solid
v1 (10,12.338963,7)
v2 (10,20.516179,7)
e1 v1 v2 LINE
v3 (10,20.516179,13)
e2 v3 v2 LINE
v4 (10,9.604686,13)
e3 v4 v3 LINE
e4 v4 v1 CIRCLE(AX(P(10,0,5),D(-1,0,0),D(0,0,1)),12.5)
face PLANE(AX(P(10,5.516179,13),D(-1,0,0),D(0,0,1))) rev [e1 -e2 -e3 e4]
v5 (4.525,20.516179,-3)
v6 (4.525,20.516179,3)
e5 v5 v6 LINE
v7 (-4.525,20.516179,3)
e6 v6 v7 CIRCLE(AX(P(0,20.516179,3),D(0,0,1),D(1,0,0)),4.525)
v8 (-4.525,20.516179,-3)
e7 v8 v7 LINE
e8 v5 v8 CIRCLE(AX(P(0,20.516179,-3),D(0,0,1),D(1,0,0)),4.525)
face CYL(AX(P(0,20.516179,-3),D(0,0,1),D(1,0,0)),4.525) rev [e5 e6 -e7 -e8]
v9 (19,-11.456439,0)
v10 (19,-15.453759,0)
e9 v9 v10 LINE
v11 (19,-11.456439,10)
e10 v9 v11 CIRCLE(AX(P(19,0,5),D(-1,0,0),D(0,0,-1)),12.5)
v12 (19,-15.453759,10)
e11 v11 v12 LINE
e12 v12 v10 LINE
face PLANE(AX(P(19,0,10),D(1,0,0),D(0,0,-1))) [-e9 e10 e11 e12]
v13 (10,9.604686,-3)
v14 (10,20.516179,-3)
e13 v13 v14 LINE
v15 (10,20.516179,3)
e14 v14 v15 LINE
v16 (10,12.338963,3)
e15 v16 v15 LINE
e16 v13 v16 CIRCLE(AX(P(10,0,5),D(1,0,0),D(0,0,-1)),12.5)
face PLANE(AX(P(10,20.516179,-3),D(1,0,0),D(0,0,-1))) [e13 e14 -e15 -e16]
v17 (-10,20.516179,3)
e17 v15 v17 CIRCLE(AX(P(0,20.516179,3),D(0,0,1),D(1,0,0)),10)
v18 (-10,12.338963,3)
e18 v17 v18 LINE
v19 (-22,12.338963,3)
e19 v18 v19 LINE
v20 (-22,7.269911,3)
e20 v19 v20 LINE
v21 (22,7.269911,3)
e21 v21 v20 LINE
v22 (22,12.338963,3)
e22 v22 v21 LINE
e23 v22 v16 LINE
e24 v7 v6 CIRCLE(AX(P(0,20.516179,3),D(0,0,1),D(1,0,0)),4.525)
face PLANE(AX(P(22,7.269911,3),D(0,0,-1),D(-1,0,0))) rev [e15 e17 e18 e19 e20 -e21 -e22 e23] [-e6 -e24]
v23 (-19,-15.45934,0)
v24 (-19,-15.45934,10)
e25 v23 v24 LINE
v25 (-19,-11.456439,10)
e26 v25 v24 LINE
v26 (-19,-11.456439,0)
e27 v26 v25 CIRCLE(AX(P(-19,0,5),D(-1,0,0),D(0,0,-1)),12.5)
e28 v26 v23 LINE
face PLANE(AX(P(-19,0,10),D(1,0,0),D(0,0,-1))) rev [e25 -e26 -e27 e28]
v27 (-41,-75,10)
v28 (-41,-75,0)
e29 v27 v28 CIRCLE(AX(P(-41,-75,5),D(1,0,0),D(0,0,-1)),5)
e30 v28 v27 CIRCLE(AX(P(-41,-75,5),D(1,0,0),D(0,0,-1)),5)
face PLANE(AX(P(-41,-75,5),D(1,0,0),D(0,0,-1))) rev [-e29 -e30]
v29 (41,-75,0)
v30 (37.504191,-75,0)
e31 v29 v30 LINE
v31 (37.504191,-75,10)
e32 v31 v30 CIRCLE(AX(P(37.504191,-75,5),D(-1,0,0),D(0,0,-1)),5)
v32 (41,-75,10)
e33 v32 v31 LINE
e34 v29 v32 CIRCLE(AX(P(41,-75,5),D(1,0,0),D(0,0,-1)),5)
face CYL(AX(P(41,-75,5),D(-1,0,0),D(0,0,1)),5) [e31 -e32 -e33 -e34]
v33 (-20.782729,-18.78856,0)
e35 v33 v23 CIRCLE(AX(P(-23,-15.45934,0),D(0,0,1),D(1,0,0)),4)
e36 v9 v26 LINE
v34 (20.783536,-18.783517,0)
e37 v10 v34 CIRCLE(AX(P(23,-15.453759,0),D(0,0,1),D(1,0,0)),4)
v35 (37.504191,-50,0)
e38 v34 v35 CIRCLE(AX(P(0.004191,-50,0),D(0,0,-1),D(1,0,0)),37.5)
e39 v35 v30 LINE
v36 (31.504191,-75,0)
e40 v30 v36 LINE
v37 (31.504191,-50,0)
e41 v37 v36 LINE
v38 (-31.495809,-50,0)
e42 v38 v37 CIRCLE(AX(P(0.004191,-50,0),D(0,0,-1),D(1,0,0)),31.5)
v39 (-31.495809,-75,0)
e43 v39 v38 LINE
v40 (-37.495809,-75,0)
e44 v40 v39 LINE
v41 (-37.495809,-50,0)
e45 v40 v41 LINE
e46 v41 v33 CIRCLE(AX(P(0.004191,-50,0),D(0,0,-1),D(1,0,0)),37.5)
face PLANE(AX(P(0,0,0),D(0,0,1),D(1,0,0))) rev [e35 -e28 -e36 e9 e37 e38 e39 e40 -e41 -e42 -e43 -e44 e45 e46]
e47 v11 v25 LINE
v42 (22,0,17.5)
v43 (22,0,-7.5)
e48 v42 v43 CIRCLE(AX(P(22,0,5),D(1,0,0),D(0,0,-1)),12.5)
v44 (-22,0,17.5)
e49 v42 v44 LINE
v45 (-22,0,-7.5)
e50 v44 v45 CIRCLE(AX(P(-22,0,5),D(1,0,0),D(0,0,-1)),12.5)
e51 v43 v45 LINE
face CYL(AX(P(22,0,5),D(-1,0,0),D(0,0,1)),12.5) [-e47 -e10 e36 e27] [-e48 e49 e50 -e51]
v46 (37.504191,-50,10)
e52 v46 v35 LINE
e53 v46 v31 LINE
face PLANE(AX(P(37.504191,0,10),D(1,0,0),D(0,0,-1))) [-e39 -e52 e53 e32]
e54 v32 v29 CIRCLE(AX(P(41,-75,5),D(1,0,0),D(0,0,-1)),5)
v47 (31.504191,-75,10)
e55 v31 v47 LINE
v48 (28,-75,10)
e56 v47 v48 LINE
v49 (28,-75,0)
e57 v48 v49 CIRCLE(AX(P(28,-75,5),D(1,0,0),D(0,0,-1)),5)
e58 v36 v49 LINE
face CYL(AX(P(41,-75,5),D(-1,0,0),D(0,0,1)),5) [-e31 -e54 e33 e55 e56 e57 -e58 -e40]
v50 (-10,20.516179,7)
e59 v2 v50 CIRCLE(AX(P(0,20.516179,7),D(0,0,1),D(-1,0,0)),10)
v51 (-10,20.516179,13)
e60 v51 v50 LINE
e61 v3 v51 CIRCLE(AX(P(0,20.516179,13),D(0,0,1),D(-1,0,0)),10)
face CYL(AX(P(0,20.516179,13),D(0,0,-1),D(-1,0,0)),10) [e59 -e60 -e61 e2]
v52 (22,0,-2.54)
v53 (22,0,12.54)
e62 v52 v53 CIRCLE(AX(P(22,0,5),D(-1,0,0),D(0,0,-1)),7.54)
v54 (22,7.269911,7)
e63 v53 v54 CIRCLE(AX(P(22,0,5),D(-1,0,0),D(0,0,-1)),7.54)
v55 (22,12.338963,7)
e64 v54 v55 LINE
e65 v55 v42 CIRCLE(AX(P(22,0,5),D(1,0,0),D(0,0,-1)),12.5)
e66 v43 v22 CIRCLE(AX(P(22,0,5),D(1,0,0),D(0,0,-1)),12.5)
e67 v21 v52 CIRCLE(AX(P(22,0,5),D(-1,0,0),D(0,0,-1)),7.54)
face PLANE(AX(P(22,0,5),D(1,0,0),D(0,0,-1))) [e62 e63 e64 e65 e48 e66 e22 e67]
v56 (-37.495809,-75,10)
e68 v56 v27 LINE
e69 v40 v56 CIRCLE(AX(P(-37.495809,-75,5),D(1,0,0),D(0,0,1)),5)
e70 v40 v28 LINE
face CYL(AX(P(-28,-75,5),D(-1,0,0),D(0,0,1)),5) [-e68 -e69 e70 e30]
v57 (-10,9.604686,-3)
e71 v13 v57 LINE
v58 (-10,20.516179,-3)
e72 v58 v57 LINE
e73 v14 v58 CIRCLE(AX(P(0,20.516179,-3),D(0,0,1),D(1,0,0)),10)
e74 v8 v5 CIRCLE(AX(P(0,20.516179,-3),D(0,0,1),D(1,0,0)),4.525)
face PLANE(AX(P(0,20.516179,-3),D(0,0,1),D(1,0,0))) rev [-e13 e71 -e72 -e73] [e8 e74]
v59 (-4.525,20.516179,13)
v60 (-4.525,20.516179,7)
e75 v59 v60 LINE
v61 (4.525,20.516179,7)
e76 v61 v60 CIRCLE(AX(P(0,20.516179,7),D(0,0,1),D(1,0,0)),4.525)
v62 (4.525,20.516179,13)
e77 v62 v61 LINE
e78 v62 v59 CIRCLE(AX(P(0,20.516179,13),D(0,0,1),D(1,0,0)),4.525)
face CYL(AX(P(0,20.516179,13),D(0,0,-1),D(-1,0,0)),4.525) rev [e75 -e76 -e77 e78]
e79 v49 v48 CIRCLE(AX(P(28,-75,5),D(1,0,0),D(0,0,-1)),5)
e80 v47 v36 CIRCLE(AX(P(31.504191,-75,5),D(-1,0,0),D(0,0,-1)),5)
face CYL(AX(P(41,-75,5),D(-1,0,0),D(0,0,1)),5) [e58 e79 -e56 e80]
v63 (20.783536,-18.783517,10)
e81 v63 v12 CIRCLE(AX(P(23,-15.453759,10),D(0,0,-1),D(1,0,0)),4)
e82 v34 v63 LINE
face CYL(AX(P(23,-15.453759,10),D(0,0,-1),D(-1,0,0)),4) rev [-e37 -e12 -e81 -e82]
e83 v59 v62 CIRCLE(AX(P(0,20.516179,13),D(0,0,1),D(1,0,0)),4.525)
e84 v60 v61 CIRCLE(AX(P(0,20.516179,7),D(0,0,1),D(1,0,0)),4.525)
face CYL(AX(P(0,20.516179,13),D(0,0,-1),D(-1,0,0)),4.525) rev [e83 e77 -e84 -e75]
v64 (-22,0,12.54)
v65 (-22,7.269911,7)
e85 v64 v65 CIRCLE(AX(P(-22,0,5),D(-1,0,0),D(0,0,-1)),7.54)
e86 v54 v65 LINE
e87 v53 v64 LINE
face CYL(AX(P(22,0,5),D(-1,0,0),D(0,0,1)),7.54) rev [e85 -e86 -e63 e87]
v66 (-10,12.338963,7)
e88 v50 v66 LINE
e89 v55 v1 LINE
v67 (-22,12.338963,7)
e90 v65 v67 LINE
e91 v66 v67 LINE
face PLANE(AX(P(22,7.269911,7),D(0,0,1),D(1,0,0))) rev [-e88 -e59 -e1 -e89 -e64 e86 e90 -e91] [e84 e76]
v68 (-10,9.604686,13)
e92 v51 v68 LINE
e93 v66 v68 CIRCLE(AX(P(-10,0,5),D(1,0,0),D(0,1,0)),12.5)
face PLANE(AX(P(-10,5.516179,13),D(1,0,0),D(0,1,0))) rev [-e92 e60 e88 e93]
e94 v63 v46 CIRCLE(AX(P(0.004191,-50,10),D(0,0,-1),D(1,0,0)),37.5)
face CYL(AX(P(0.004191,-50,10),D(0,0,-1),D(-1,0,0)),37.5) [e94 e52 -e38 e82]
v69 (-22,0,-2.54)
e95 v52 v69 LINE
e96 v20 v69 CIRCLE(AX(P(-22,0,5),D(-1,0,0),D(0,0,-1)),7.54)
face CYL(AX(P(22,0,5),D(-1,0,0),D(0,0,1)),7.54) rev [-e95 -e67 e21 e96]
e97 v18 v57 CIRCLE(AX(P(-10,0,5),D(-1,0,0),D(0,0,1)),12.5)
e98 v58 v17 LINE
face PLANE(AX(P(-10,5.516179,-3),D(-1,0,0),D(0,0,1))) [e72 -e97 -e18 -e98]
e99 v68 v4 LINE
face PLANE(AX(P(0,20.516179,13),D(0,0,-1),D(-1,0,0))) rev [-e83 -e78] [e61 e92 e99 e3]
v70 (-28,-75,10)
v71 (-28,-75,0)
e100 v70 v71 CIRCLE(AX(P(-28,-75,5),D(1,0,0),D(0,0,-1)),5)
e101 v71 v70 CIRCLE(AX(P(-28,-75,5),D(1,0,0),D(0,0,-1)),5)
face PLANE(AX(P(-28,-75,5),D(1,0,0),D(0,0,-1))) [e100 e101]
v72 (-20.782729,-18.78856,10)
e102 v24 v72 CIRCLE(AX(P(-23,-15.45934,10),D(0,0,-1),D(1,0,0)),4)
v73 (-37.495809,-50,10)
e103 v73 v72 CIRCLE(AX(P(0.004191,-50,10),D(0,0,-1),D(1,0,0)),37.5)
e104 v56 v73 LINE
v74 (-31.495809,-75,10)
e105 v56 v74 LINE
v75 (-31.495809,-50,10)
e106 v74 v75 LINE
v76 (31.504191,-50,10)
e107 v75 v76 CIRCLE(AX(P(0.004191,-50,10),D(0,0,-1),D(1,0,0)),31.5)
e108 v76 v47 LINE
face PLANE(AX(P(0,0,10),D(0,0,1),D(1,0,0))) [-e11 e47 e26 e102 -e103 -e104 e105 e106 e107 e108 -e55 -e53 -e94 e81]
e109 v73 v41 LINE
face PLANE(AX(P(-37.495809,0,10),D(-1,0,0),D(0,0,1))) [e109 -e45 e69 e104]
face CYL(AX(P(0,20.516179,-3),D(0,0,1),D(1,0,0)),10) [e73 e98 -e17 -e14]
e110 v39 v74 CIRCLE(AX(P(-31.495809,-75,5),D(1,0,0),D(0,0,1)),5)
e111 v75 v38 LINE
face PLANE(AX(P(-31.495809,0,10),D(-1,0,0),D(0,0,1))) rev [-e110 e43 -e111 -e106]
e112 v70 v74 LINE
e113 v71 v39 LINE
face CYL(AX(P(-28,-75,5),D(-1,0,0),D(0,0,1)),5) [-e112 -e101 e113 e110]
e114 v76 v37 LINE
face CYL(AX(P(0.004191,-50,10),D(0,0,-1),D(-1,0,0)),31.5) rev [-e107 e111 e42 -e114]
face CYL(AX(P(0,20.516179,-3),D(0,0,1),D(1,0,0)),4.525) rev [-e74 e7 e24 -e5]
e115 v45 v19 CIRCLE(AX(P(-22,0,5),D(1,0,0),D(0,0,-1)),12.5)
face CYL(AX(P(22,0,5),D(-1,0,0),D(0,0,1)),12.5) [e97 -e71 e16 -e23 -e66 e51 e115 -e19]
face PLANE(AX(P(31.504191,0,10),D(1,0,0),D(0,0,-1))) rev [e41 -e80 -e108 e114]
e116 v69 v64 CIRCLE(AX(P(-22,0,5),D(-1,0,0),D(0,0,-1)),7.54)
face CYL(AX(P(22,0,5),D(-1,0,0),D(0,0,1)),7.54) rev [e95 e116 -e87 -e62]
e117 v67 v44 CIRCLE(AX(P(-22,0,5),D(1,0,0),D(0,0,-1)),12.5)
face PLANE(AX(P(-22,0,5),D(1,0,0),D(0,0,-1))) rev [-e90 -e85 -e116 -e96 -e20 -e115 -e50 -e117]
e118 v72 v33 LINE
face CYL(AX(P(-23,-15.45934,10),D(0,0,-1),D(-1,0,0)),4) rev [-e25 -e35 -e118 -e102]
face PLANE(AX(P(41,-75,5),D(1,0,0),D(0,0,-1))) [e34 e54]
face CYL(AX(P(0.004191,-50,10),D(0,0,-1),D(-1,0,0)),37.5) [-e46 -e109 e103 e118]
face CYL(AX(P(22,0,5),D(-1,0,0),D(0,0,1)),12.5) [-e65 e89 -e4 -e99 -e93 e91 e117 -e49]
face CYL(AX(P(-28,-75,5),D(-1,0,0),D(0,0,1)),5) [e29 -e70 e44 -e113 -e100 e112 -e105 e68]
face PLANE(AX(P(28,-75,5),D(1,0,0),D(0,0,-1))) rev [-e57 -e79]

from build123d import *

# Parameters (mm, degrees)
U_FORK_PLATE_DEPTH      = 10
SPLIT_COLLAR_DEPTH      = 22
COLLAR_BORE_SKETCH_R    = 7.54
COLLAR_BORE_DEPTH       = 44
EYE_LUG_FRONT_SKETCH_R  = 4.525
EYE_LUG_FRONT_DEPTH     = 6
EYE_START               = -6
EYE_LUG_REAR_SKETCH_R   = 4.525
EYE_LUG_REAR_DEPTH      = 6
EYE_START_2             = -30
EYE_HOLE_SKETCH_R       = 7.54
EYE_CROSS_HOLE_DEPTH    = 30
FORK_PIN_A_SKETCH_R     = 5
FORK_PIN_A_10_DEPTH     = 6.5
FORK_PIN_B_SKETCH_R     = 5
FORK_PIN_B_10_DEPTH     = 6.5
FORK_EDGE_FILLET_R4_A_R = 4
FORK_EDGE_FILLET_R4_B_R = 4


with BuildPart() as part:
    # U-Fork Profile Sketch → U-Fork Plate (new body)
    with BuildSketch(Plane.XY):
        with BuildLine():
            ThreePointArc((19, -17.667211171), (32.551025104, -31.373310069), (37.504190816, -50))
            Line((37.504190816, -50), (37.504190816, -75))
            Line((37.504190816, -75), (31.504190816, -75))
            Line((31.504190816, -75), (31.504190816, -50))
            ThreePointArc((31.504190816, -50), (0.004190816, -18.5), (-31.495809184, -50))
            Line((-31.495809184, -50), (-31.495809184, -75))
            Line((-31.495809184, -75), (-37.495809184, -75))
            Line((-37.495809184, -75), (-37.495809184, -50))
            ThreePointArc((-37.495809184, -50), (-32.545057682, -31.377529106), (-19, -17.672136918))
            Line((-19, -17.672136918), (-19, 0))
            Line((-19, 0), (19, 0))
            Line((19, 0), (19, -17.667211171))
        make_face()
    extrude(amount=U_FORK_PLATE_DEPTH)

    # Collar Sketch → Split Collar (add, symmetric)
    with BuildSketch(Plane(origin=(0, 0, 0), x_dir=(0, 0, -1), z_dir=(1, 0, 0))):
        with BuildLine():
            Line((-7, 7.269910591), (-7, 12.338962679))
            ThreePointArc((-7, 12.338962679), (-5, -12.5), (-3, 12.338962679))
            Line((-3, 12.338962679), (-3, 7.269910591))
            ThreePointArc((-3, 7.269910591), (-5, -7.54), (-7, 7.269910591))
        make_face()
    extrude(amount=SPLIT_COLLAR_DEPTH, both=True)

    # Collar Bore Sketch → Collar Bore (cut)
    with BuildSketch(Plane(origin=(19, 0, 0), x_dir=(0, 0, -1), z_dir=(1, 0, 0))):
        with Locations((-5, 0)):
            Circle(COLLAR_BORE_SKETCH_R)
    extrude(amount=-COLLAR_BORE_DEPTH, mode=Mode.SUBTRACT)

    # Eye Lug Front Sketch → Eye Lug Front (add)
    with BuildSketch(Plane.XY.offset(7)):
        with BuildLine():
            Line((-10, 5.516178569), (10, 5.516178569))
            Line((10, 5.516178569), (10, 20.516178569))
            ThreePointArc((10, 20.516178569), (0, 30.516178569), (-10, 20.516178569))
            Line((-10, 20.516178569), (-10, 5.516178569))
        make_face()
        with Locations((0, 20.516178569)):
            Circle(EYE_LUG_FRONT_SKETCH_R, mode=Mode.SUBTRACT)
    extrude(amount=EYE_LUG_FRONT_DEPTH)

    # Eye Lug Rear Sketch → Eye Lug Rear (add)
    with BuildSketch(Plane.XY.offset(3).offset(EYE_START)):
        with BuildLine():
            Line((10, 20.516178569), (10, 5.516178569))
            Line((10, 5.516178569), (-10, 5.516178569))
            Line((-10, 5.516178569), (-10, 20.516178569))
            ThreePointArc((-10, 20.516178569), (0, 30.516178569), (10, 20.516178569))
        make_face()
        with Locations((0, 20.516178569)):
            Circle(EYE_LUG_REAR_SKETCH_R, mode=Mode.SUBTRACT)
    extrude(amount=EYE_LUG_REAR_DEPTH)

    # Eye Hole Sketch → Eye Cross Hole (cut)
    with BuildSketch(Plane.ZY.offset(10).offset(EYE_START_2)):
        with Locations((5, 0)):
            Circle(EYE_HOLE_SKETCH_R)
    extrude(amount=EYE_CROSS_HOLE_DEPTH, mode=Mode.SUBTRACT)

    # Fork Pin A Sketch → Fork Pin A Ø10 (add, symmetric)
    with BuildSketch(Plane(origin=(34.5, 0, 0), x_dir=(0, 0, -1), z_dir=(1, 0, 0))):
        with Locations((-5, -75)):
            Circle(FORK_PIN_A_SKETCH_R)
    extrude(amount=FORK_PIN_A_10_DEPTH, both=True)

    # Fork Pin B Sketch → Fork Pin B Ø10 (add, symmetric)
    with BuildSketch(Plane(origin=(-34.5, 0, 0), x_dir=(0, 0, -1), z_dir=(1, 0, 0))):
        with Locations((-5, -75)):
            Circle(FORK_PIN_B_SKETCH_R)
    extrude(amount=FORK_PIN_B_10_DEPTH, both=True)

    # Fork Edge Fillet R4 A
    fork_edge_fillet_r4_a_edges = [part.edges().sort_by_distance(p)[0] for p in [
        (19, -17.667211171, 5),
    ]]
    fillet(fork_edge_fillet_r4_a_edges, radius=FORK_EDGE_FILLET_R4_A_R)

    # Fork Edge Fillet R4 B
    fork_edge_fillet_r4_b_edges = [part.edges().sort_by_distance(p)[0] for p in [
        (-19, -17.672136918, 5),
    ]]
    fillet(fork_edge_fillet_r4_b_edges, radius=FORK_EDGE_FILLET_R4_B_R)


solid = part.part
